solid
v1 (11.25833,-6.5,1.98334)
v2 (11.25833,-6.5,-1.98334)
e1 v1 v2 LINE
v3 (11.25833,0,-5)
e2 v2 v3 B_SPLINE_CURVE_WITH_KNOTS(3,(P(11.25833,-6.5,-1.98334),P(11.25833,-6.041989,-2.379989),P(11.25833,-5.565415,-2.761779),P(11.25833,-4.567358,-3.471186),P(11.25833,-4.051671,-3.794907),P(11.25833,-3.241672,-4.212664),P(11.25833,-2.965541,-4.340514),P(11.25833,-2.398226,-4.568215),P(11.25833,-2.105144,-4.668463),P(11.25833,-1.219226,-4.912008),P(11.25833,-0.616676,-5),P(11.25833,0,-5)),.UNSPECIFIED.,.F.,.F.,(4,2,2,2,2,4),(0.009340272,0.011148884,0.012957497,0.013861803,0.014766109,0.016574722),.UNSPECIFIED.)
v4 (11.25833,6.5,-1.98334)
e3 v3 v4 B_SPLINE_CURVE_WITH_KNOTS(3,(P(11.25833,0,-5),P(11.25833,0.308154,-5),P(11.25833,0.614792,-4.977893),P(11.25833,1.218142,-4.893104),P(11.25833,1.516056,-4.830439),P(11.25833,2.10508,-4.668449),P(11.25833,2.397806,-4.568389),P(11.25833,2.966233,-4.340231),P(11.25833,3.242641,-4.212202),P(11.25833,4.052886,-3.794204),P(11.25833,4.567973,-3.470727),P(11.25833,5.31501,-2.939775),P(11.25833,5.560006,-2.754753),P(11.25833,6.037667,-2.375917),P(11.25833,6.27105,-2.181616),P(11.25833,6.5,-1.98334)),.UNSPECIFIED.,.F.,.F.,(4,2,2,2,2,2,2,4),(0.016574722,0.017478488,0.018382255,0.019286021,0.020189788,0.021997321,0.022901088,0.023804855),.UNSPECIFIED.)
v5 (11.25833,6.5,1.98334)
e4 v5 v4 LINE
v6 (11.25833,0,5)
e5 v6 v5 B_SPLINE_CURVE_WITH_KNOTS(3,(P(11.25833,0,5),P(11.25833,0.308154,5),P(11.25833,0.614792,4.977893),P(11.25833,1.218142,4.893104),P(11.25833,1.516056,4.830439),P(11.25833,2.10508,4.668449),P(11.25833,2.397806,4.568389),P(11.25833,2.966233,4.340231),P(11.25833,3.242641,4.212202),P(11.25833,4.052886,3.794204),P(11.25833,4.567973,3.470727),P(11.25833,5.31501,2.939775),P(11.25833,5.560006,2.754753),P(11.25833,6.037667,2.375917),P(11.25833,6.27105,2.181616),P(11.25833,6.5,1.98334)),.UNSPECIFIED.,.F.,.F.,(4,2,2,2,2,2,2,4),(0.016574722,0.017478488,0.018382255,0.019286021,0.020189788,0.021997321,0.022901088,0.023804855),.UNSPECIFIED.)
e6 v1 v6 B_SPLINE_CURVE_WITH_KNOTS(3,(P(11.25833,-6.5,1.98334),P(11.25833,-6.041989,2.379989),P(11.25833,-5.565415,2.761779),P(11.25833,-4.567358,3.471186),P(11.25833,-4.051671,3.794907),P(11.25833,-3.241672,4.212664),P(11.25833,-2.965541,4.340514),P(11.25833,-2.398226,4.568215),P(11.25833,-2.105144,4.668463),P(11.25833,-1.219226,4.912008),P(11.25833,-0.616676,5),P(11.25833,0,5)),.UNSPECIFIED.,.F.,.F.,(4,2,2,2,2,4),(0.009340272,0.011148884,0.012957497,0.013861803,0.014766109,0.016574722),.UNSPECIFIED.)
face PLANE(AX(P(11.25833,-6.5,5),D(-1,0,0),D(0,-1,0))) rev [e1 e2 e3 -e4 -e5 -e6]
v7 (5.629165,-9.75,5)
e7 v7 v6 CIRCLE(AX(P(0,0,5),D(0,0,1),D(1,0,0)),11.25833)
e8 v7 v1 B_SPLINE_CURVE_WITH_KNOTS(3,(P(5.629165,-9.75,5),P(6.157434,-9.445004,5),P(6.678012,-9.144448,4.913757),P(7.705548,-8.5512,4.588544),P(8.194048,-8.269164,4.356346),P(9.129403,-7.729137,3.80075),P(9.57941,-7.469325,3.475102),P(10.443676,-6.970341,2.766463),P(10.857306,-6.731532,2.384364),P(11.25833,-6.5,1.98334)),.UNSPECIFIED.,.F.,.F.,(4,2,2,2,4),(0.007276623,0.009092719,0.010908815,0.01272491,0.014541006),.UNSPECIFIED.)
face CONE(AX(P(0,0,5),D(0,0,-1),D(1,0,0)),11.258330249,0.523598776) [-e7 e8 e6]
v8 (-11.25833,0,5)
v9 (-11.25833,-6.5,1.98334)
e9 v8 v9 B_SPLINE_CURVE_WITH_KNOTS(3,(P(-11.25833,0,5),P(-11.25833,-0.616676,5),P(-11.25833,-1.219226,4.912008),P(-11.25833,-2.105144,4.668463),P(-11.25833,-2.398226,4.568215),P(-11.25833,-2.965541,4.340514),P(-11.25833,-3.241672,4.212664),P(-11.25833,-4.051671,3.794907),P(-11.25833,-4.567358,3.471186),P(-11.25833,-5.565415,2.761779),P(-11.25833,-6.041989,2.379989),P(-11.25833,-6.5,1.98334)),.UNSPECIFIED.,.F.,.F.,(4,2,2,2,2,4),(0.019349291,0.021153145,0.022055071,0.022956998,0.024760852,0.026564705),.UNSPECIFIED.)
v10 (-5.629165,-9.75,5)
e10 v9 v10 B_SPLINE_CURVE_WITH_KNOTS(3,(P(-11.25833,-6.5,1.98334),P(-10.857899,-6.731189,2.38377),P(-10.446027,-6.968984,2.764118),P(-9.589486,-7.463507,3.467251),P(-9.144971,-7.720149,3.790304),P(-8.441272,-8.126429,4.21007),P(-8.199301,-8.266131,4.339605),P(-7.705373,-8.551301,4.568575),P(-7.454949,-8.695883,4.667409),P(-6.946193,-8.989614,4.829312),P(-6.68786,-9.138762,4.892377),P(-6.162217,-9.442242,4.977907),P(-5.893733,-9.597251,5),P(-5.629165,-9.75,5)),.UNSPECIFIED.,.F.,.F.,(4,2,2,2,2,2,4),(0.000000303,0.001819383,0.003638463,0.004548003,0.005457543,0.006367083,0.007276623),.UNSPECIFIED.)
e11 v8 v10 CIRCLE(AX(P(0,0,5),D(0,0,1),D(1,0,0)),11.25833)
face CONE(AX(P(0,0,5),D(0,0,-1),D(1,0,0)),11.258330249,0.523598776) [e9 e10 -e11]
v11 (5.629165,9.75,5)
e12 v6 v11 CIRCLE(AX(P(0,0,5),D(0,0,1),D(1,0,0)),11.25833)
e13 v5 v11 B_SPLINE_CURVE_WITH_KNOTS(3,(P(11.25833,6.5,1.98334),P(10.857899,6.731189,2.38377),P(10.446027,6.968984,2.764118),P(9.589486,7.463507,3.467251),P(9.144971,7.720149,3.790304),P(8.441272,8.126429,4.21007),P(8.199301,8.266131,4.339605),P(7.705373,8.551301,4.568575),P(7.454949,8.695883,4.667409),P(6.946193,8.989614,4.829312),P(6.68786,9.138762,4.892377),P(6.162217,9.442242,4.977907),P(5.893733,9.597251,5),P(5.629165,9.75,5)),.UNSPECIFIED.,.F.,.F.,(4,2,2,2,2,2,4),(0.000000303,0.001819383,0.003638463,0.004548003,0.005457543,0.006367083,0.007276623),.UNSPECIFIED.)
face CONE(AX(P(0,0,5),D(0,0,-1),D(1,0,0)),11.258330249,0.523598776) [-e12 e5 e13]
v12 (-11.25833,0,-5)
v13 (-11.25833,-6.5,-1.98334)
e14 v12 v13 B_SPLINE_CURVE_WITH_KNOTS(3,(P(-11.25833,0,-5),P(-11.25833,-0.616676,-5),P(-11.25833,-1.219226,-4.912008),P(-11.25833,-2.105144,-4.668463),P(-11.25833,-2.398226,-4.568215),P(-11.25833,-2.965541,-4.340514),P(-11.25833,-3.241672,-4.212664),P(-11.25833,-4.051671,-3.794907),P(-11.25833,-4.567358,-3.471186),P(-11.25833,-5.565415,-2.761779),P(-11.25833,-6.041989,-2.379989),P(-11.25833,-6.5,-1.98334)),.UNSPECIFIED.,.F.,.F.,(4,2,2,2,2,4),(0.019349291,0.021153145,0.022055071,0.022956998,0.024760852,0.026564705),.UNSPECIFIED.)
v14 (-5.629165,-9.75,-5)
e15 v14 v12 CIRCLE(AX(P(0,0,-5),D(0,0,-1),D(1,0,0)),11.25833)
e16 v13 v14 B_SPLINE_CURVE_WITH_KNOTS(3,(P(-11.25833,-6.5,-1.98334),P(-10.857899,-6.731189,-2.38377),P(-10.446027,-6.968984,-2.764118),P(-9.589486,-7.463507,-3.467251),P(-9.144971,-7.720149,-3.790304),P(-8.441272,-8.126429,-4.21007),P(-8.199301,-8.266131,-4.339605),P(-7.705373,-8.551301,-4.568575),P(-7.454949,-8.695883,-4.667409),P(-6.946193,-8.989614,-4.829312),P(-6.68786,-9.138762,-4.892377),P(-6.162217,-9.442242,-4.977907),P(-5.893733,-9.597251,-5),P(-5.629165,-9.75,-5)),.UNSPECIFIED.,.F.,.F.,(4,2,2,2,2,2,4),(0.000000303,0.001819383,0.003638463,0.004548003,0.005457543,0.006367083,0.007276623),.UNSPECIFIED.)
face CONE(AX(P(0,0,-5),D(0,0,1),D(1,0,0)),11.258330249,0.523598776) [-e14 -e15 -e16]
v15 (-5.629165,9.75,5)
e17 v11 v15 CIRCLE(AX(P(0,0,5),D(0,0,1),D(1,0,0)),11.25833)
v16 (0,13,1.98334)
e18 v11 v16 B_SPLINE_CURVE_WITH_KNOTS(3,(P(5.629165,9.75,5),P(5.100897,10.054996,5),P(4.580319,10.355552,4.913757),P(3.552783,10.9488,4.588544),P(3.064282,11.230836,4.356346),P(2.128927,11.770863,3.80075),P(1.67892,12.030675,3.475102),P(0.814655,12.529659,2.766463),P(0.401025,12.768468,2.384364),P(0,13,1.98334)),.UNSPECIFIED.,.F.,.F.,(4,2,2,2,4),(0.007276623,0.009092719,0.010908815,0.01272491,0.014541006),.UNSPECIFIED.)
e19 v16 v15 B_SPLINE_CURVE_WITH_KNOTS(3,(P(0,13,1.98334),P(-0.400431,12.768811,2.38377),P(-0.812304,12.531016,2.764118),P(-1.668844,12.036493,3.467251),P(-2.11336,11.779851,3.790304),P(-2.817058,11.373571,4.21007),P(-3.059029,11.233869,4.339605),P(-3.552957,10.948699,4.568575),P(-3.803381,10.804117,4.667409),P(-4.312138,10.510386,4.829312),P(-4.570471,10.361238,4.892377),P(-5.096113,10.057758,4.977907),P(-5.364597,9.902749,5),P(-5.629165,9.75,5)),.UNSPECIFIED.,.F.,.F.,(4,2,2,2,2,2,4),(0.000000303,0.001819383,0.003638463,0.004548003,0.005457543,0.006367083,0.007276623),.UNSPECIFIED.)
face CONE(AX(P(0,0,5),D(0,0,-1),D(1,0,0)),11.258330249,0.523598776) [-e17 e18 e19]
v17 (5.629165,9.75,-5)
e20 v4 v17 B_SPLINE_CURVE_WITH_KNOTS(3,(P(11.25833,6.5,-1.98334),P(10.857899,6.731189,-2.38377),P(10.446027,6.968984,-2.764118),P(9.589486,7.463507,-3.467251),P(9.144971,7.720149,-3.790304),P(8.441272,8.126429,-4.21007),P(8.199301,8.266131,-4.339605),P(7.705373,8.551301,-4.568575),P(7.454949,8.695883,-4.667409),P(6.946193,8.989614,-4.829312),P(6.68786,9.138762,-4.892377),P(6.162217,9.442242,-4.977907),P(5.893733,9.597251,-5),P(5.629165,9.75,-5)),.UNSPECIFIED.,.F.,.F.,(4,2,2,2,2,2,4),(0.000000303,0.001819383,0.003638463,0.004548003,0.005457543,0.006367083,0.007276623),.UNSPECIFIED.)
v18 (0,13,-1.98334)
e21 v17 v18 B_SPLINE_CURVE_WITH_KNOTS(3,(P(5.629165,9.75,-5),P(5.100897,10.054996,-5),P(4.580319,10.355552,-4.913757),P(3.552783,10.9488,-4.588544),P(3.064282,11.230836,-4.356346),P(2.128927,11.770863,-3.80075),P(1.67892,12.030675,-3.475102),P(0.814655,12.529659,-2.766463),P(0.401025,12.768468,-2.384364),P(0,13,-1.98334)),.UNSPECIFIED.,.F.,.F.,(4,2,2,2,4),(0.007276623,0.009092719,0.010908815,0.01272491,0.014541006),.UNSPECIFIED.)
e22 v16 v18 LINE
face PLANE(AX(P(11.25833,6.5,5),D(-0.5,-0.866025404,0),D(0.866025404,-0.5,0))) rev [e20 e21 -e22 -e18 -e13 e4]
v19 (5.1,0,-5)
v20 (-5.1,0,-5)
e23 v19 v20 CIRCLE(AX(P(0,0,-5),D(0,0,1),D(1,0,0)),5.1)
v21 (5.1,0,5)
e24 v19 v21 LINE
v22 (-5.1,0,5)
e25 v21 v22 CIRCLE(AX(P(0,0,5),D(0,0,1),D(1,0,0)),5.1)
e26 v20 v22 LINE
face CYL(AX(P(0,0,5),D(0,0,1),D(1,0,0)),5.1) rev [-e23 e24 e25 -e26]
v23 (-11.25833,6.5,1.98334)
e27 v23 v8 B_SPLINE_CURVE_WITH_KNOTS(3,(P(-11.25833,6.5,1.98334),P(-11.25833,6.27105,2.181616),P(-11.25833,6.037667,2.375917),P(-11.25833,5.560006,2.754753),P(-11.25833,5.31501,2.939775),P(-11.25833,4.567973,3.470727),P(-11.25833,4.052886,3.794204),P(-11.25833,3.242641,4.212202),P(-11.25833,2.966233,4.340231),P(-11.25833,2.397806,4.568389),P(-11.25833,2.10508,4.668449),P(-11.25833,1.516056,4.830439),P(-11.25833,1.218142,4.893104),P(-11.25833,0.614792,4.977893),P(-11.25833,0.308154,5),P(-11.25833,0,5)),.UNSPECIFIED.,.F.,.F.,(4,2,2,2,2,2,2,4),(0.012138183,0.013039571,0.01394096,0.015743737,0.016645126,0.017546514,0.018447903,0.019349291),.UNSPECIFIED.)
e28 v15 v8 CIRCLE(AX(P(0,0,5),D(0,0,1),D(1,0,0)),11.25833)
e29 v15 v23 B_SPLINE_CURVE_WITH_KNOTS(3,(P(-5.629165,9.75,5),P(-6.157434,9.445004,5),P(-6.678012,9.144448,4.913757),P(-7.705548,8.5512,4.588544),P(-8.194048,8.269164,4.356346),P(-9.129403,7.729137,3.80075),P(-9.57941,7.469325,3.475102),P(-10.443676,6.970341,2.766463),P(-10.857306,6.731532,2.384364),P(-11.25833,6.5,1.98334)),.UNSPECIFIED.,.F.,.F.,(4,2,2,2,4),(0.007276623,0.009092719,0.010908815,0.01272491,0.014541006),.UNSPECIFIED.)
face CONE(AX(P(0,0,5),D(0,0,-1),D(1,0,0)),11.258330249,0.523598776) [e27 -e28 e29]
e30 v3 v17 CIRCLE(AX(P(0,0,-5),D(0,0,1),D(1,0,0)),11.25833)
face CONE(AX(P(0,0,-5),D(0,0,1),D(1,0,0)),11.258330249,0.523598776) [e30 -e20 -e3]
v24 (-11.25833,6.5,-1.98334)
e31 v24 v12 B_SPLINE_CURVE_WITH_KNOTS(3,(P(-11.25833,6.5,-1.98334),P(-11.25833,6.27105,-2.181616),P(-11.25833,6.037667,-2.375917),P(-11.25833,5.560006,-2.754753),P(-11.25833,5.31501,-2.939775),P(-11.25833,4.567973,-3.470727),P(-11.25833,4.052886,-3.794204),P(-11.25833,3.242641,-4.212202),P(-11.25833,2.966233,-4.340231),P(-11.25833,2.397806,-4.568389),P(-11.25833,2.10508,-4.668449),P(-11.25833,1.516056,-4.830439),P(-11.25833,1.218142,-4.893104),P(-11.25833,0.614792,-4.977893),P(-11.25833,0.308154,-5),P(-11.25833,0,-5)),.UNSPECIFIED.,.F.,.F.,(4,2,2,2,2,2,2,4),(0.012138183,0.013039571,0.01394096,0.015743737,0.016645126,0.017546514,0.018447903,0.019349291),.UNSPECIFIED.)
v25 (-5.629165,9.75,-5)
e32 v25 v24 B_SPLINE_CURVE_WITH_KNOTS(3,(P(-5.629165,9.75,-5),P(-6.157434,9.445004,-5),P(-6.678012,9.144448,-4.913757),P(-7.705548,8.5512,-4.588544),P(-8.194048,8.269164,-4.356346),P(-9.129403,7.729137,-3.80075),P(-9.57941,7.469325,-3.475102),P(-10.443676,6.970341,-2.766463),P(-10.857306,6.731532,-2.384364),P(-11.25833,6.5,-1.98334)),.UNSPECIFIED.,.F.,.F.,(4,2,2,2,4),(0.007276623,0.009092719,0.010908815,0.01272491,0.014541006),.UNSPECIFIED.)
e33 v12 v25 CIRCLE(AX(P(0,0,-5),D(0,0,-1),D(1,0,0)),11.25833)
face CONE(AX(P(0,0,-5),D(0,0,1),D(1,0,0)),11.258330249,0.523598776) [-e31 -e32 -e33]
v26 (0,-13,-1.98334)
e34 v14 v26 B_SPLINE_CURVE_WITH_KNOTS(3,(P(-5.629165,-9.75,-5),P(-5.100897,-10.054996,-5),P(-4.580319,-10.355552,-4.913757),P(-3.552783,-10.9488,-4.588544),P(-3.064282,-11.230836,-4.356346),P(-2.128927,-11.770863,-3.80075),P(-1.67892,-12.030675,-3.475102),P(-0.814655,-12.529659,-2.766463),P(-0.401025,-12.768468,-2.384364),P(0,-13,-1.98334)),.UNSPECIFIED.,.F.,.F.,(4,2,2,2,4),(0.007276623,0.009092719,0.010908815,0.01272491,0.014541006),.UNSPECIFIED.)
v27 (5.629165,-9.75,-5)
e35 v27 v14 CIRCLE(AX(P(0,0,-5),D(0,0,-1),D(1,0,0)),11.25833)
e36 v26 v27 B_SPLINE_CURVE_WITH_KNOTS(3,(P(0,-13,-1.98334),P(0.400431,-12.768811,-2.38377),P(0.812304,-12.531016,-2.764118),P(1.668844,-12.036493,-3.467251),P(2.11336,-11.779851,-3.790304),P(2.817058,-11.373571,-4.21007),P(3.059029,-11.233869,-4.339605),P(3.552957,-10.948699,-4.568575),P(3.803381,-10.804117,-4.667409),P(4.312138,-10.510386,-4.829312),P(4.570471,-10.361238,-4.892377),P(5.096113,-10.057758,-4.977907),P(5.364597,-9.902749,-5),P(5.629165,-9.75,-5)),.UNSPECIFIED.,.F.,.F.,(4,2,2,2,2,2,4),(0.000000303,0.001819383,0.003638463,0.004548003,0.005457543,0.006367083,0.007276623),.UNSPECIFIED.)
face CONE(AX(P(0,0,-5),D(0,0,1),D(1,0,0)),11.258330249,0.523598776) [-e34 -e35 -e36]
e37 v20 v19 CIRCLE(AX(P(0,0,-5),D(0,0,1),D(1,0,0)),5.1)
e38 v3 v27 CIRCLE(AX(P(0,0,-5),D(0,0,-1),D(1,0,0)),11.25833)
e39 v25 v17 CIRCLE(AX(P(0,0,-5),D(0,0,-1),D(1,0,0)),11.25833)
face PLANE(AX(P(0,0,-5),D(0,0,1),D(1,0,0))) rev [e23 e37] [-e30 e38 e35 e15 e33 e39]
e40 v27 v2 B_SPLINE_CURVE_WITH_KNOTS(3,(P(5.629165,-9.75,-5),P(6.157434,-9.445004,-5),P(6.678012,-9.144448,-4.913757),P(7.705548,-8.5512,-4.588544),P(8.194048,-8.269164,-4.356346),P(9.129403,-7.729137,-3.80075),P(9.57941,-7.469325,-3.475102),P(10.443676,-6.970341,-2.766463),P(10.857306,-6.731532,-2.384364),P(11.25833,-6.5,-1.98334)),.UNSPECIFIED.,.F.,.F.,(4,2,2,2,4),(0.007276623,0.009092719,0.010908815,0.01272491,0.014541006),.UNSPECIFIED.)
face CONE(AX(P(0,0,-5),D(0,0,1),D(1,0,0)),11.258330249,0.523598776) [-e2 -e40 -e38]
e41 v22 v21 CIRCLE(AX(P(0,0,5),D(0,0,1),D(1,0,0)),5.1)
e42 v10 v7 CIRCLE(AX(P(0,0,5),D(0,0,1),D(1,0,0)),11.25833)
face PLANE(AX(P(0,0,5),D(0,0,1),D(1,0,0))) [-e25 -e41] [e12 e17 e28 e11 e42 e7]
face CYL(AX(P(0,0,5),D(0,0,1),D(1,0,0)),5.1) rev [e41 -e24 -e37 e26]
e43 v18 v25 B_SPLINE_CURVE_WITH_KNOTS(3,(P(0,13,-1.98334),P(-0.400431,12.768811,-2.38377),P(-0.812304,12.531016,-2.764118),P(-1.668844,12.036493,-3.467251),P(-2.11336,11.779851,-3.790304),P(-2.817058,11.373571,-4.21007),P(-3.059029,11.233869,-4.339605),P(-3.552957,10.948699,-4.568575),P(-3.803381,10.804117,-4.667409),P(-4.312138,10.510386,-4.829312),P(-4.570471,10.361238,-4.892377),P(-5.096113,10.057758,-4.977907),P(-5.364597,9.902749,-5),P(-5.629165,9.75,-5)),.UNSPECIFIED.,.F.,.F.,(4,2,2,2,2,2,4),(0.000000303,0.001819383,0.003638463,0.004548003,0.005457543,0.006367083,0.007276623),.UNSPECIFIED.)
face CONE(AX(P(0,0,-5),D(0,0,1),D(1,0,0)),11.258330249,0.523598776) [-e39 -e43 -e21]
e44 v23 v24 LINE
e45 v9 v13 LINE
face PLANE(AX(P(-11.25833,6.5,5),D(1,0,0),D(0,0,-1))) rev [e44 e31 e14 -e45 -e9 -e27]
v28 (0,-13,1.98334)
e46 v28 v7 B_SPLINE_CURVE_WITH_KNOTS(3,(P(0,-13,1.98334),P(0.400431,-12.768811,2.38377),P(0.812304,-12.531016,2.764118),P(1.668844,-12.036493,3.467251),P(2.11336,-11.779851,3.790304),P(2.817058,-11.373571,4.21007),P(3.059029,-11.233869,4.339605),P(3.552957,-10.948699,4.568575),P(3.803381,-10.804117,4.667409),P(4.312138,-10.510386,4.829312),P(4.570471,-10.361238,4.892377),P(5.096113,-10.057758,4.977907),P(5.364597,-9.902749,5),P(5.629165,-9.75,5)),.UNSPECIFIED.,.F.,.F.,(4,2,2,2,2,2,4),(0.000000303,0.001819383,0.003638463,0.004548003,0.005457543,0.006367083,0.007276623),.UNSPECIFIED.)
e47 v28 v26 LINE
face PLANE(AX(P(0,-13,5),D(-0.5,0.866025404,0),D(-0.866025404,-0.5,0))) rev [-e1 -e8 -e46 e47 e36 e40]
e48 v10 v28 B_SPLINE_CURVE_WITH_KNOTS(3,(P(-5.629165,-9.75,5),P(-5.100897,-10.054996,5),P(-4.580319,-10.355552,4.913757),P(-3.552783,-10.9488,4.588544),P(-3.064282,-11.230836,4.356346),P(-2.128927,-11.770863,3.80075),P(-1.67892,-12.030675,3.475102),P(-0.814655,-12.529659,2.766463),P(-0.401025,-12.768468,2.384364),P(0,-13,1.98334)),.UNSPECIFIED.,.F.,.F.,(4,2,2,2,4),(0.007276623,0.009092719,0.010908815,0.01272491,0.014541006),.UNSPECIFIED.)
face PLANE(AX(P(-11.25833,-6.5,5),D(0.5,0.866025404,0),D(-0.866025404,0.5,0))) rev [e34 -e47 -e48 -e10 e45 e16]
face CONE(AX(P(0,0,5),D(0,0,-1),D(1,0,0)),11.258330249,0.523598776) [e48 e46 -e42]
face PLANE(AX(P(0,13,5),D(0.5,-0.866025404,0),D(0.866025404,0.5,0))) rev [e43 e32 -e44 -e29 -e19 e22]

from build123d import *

# Parameters (mm, degrees)
BOSS_EXTRUDE1_DEPTH     = 5
SKETCH2_OUTSIDE_W       = 43.226
SKETCH2_OUTSIDE_H       = 46.71
SKETCH2_OUTSIDE_R       = 11.258330249
CUT_EXTRUDE1_DEPTH      = 10
CUT_EXTRUDE1_DRAFT      = -30
MIRROR1_COPY_1_SKETCH_W = 43.226
MIRROR1_COPY_1_SKETCH_H = 46.71
MIRROR1_COPY_1_SKETCH_R = 11.258330249
MIRROR1_COPY_1_DEPTH    = 10
MIRROR1_COPY_1_DRAFT    = -30
M12_TAPPED_HOLE3_D      = 10.2
M12_TAPPED_HOLE3_DEPTH  = 38.75


with BuildPart() as part:
    # Sketch1 → Boss-Extrude1 (new, symmetric)
    with BuildSketch(Plane.XY):
        Polygon((0, 13), (-11.258330249, 6.5), (-11.258330249, -6.5), (0, -13), (11.258330249, -6.5), (11.258330249, 6.5), align=None)
    extrude(amount=BOSS_EXTRUDE1_DEPTH, both=True)


with BuildPart() as cut_extrude1_tool:
    # Sketch2 outside → Cut-Extrude1 (with draft: the straight prism first)
    with BuildSketch(Plane.XY.offset(5)):
        Rectangle(SKETCH2_OUTSIDE_W, SKETCH2_OUTSIDE_H)
        Circle(SKETCH2_OUTSIDE_R, mode=Mode.SUBTRACT)
    extrude(amount=-CUT_EXTRUDE1_DEPTH)
    # Cut-Extrude1: the draft: its side faces are tilted about the plane it starts from
    cut_extrude1_sides = [cut_extrude1_tool.faces().sort_by_distance(p)[0] for p in [
        (0, -23.355, 0),
        (21.613, 0, 0),
        (0, 23.355, 0),
        (-21.613, 0, 0),
        (-11.258330249, 0, 0),
    ]]
    draft(cut_extrude1_sides, Plane.XY.offset(5), CUT_EXTRUDE1_DRAFT)


with BuildPart() as part_1:
    add(part.part)

    # Cut-Extrude1: cut by cut_extrude1_tool
    add(cut_extrude1_tool.part, mode=Mode.SUBTRACT)


with BuildPart() as mirror1_copy_1_tool:
    # Mirror1 copy 1 sketch → Mirror1 copy 1 (with draft: the straight prism first)
    with BuildSketch(Plane(origin=(0, 0, -5), x_dir=(1, 0, 0), z_dir=(0, 0, -1))):
        Rectangle(MIRROR1_COPY_1_SKETCH_W, MIRROR1_COPY_1_SKETCH_H)
        Circle(MIRROR1_COPY_1_SKETCH_R, mode=Mode.SUBTRACT)
    extrude(amount=-MIRROR1_COPY_1_DEPTH)
    # Mirror1 copy 1: the draft: its side faces are tilted about the plane it starts from
    mirror1_copy_1_sides = [mirror1_copy_1_tool.faces().sort_by_distance(p)[0] for p in [
        (0, -23.355, 0),
        (21.613, 0, 0),
        (0, 23.355, 0),
        (-21.613, 0, 0),
        (-11.258330249, 0, 0),
    ]]
    draft(mirror1_copy_1_sides, Plane(origin=(0, 0, -5), x_dir=(1, 0, 0), z_dir=(0, 0, -1)), MIRROR1_COPY_1_DRAFT)


with BuildPart() as part_2:
    add(part_1.part)

    # Mirror1 copy 1: cut by mirror1_copy_1_tool
    add(mirror1_copy_1_tool.part, mode=Mode.SUBTRACT)

    # M12 Tapped Hole3
    with Locations(Plane.XY.offset(5)):
        with Locations((0, 0)):
            Hole(M12_TAPPED_HOLE3_D / 2, depth=M12_TAPPED_HOLE3_DEPTH)


solid = part_2.part
